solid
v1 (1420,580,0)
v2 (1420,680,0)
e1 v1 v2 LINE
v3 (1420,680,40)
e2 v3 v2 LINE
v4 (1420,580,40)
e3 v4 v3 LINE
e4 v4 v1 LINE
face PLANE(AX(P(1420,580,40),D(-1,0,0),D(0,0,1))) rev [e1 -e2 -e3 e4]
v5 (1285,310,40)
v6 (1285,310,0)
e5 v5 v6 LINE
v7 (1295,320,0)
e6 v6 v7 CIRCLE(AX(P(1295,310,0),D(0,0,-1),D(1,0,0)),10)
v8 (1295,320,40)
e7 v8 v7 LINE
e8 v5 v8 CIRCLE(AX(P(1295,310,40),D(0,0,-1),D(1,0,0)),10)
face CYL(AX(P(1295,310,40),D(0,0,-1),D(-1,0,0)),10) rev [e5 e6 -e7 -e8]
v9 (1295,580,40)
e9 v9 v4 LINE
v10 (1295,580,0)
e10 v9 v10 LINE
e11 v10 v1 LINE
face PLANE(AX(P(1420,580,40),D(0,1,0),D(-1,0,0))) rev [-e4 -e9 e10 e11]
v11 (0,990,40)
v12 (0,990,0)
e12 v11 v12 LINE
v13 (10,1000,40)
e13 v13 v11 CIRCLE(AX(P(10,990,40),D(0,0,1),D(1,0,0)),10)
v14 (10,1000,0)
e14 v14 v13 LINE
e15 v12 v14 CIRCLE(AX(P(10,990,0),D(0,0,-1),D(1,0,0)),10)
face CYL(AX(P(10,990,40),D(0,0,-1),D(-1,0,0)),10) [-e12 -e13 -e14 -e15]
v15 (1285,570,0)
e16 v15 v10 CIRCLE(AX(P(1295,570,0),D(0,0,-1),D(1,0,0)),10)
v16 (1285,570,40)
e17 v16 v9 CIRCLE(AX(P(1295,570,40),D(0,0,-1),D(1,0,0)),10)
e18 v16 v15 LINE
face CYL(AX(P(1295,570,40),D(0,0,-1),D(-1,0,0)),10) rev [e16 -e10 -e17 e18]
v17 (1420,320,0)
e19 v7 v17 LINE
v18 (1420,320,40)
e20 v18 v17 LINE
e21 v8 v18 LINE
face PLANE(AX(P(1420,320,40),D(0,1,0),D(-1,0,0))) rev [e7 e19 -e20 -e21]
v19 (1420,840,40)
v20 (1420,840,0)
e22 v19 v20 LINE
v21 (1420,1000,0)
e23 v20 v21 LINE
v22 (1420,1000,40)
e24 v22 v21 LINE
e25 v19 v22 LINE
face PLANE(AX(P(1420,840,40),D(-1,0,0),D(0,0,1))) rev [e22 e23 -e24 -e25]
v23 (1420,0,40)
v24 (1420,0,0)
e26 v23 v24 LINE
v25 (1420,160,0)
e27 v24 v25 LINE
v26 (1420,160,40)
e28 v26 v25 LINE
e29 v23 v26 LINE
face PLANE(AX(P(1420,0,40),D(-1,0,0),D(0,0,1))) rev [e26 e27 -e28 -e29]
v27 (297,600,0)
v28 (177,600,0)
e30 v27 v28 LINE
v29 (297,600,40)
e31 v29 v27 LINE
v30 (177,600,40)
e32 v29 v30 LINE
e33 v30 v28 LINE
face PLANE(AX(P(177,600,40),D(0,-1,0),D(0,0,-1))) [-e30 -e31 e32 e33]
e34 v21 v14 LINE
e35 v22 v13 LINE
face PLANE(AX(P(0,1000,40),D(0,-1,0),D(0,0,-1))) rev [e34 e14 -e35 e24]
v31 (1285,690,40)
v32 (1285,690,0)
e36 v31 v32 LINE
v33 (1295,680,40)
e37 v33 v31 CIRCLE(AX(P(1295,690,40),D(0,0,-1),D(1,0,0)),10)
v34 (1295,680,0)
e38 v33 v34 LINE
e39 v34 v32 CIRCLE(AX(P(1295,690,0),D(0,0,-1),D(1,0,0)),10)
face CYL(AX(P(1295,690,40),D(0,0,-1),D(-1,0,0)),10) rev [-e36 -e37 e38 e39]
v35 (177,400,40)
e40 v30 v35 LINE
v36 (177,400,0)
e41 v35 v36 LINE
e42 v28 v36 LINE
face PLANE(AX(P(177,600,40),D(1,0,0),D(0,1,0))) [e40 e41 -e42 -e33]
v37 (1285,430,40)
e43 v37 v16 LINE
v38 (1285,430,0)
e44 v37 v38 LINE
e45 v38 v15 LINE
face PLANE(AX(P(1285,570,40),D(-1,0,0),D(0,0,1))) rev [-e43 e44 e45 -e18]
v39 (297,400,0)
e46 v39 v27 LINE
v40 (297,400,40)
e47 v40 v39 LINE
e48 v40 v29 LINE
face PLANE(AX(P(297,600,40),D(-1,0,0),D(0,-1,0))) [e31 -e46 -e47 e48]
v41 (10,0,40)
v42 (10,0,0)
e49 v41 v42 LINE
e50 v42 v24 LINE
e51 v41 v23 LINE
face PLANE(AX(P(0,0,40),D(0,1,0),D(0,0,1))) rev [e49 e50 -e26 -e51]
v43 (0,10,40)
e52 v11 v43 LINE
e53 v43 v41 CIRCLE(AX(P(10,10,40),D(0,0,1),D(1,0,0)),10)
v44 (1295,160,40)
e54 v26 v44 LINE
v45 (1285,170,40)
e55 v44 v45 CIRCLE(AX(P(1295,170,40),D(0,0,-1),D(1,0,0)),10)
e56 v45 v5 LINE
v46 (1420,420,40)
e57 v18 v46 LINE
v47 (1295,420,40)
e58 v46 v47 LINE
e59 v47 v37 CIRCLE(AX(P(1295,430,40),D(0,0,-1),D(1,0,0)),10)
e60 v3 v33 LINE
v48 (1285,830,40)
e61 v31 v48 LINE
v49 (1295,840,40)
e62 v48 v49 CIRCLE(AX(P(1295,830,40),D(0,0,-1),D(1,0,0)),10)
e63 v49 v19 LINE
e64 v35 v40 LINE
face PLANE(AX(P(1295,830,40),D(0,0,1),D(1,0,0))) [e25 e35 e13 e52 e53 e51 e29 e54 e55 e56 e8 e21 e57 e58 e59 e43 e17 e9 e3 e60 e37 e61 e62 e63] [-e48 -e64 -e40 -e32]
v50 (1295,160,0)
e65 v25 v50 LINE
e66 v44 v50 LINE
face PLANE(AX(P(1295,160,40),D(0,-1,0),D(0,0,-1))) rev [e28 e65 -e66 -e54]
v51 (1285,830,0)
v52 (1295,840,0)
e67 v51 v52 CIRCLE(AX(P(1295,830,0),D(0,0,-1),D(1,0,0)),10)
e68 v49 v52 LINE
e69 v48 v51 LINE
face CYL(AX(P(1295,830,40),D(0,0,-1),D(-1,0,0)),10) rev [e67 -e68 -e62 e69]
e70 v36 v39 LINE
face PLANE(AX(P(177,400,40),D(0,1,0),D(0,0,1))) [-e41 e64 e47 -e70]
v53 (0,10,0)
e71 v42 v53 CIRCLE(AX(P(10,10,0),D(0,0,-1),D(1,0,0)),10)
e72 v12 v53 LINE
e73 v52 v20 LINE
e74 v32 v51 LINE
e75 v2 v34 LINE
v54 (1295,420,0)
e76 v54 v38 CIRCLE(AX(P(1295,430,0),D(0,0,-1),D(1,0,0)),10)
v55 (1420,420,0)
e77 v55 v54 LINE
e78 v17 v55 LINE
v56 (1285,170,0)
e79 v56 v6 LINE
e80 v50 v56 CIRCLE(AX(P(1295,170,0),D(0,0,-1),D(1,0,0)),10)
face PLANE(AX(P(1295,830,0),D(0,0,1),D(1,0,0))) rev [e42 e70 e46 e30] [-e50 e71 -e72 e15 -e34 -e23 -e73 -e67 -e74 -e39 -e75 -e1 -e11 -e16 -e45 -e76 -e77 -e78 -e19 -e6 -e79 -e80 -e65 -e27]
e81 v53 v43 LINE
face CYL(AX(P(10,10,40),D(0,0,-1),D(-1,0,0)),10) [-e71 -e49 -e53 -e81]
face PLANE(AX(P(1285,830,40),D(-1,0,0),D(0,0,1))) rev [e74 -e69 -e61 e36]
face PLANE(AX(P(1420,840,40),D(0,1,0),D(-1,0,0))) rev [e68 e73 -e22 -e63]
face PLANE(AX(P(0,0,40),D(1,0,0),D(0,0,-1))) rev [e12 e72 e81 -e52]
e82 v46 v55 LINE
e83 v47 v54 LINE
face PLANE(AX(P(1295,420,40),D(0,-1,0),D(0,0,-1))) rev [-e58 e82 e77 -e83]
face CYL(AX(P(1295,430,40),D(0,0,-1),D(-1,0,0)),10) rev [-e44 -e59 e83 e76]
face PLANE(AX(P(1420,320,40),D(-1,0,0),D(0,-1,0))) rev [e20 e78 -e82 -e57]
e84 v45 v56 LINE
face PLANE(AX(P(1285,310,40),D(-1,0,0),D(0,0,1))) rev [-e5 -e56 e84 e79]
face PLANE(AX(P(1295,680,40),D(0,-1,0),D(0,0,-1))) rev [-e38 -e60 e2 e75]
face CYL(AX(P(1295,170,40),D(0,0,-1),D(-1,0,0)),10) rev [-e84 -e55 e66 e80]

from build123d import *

# Parameters (mm, degrees)
SKETCH1_W           = 120
SKETCH1_H           = 200
BOSS_EXTRUDE1_DEPTH = 40
FILLET1_R           = 10


with BuildPart() as part:
    # Sketch1 → Boss-Extrude1 (new body)
    with BuildSketch(Plane.XY):
        with BuildLine():
            Line((1420, 840), (1295, 840))
            ThreePointArc((1295, 840), (1287.928932188, 837.071067812), (1285, 830))
            Line((1285, 830), (1285, 690))
            ThreePointArc((1285, 690), (1287.928932188, 682.928932188), (1295, 680))
            Line((1295, 680), (1420, 680))
            Line((1420, 680), (1420, 580))
            Line((1420, 580), (1295, 580))
            ThreePointArc((1295, 580), (1287.928932188, 577.071067812), (1285, 570))
            Line((1285, 570), (1285, 430))
            ThreePointArc((1285, 430), (1287.928932188, 422.928932188), (1295, 420))
            Line((1295, 420), (1420, 420))
            Line((1420, 420), (1420, 320))
            Line((1420, 320), (1295, 320))
            ThreePointArc((1295, 320), (1287.928932188, 317.071067812), (1285, 310))
            Line((1285, 310), (1285, 170))
            ThreePointArc((1285, 170), (1287.928932188, 162.928932188), (1295, 160))
            Line((1295, 160), (1420, 160))
            Line((1420, 160), (1420, 0))
            Line((1420, 0), (0, 0))
            Line((0, 0), (0, 1000))
            Line((0, 1000), (1420, 1000))
            Line((1420, 1000), (1420, 840))
        make_face()
        with Locations((237, 500)):
            Rectangle(SKETCH1_W, SKETCH1_H, mode=Mode.SUBTRACT)
    extrude(amount=BOSS_EXTRUDE1_DEPTH)

    # Fillet1
    fillet1_edges = [part.edges().sort_by_distance(p)[0] for p in [
        (0, 1000, 20),
        (0, 0, 20),
    ]]
    fillet(fillet1_edges, radius=FILLET1_R)


solid = part.part
